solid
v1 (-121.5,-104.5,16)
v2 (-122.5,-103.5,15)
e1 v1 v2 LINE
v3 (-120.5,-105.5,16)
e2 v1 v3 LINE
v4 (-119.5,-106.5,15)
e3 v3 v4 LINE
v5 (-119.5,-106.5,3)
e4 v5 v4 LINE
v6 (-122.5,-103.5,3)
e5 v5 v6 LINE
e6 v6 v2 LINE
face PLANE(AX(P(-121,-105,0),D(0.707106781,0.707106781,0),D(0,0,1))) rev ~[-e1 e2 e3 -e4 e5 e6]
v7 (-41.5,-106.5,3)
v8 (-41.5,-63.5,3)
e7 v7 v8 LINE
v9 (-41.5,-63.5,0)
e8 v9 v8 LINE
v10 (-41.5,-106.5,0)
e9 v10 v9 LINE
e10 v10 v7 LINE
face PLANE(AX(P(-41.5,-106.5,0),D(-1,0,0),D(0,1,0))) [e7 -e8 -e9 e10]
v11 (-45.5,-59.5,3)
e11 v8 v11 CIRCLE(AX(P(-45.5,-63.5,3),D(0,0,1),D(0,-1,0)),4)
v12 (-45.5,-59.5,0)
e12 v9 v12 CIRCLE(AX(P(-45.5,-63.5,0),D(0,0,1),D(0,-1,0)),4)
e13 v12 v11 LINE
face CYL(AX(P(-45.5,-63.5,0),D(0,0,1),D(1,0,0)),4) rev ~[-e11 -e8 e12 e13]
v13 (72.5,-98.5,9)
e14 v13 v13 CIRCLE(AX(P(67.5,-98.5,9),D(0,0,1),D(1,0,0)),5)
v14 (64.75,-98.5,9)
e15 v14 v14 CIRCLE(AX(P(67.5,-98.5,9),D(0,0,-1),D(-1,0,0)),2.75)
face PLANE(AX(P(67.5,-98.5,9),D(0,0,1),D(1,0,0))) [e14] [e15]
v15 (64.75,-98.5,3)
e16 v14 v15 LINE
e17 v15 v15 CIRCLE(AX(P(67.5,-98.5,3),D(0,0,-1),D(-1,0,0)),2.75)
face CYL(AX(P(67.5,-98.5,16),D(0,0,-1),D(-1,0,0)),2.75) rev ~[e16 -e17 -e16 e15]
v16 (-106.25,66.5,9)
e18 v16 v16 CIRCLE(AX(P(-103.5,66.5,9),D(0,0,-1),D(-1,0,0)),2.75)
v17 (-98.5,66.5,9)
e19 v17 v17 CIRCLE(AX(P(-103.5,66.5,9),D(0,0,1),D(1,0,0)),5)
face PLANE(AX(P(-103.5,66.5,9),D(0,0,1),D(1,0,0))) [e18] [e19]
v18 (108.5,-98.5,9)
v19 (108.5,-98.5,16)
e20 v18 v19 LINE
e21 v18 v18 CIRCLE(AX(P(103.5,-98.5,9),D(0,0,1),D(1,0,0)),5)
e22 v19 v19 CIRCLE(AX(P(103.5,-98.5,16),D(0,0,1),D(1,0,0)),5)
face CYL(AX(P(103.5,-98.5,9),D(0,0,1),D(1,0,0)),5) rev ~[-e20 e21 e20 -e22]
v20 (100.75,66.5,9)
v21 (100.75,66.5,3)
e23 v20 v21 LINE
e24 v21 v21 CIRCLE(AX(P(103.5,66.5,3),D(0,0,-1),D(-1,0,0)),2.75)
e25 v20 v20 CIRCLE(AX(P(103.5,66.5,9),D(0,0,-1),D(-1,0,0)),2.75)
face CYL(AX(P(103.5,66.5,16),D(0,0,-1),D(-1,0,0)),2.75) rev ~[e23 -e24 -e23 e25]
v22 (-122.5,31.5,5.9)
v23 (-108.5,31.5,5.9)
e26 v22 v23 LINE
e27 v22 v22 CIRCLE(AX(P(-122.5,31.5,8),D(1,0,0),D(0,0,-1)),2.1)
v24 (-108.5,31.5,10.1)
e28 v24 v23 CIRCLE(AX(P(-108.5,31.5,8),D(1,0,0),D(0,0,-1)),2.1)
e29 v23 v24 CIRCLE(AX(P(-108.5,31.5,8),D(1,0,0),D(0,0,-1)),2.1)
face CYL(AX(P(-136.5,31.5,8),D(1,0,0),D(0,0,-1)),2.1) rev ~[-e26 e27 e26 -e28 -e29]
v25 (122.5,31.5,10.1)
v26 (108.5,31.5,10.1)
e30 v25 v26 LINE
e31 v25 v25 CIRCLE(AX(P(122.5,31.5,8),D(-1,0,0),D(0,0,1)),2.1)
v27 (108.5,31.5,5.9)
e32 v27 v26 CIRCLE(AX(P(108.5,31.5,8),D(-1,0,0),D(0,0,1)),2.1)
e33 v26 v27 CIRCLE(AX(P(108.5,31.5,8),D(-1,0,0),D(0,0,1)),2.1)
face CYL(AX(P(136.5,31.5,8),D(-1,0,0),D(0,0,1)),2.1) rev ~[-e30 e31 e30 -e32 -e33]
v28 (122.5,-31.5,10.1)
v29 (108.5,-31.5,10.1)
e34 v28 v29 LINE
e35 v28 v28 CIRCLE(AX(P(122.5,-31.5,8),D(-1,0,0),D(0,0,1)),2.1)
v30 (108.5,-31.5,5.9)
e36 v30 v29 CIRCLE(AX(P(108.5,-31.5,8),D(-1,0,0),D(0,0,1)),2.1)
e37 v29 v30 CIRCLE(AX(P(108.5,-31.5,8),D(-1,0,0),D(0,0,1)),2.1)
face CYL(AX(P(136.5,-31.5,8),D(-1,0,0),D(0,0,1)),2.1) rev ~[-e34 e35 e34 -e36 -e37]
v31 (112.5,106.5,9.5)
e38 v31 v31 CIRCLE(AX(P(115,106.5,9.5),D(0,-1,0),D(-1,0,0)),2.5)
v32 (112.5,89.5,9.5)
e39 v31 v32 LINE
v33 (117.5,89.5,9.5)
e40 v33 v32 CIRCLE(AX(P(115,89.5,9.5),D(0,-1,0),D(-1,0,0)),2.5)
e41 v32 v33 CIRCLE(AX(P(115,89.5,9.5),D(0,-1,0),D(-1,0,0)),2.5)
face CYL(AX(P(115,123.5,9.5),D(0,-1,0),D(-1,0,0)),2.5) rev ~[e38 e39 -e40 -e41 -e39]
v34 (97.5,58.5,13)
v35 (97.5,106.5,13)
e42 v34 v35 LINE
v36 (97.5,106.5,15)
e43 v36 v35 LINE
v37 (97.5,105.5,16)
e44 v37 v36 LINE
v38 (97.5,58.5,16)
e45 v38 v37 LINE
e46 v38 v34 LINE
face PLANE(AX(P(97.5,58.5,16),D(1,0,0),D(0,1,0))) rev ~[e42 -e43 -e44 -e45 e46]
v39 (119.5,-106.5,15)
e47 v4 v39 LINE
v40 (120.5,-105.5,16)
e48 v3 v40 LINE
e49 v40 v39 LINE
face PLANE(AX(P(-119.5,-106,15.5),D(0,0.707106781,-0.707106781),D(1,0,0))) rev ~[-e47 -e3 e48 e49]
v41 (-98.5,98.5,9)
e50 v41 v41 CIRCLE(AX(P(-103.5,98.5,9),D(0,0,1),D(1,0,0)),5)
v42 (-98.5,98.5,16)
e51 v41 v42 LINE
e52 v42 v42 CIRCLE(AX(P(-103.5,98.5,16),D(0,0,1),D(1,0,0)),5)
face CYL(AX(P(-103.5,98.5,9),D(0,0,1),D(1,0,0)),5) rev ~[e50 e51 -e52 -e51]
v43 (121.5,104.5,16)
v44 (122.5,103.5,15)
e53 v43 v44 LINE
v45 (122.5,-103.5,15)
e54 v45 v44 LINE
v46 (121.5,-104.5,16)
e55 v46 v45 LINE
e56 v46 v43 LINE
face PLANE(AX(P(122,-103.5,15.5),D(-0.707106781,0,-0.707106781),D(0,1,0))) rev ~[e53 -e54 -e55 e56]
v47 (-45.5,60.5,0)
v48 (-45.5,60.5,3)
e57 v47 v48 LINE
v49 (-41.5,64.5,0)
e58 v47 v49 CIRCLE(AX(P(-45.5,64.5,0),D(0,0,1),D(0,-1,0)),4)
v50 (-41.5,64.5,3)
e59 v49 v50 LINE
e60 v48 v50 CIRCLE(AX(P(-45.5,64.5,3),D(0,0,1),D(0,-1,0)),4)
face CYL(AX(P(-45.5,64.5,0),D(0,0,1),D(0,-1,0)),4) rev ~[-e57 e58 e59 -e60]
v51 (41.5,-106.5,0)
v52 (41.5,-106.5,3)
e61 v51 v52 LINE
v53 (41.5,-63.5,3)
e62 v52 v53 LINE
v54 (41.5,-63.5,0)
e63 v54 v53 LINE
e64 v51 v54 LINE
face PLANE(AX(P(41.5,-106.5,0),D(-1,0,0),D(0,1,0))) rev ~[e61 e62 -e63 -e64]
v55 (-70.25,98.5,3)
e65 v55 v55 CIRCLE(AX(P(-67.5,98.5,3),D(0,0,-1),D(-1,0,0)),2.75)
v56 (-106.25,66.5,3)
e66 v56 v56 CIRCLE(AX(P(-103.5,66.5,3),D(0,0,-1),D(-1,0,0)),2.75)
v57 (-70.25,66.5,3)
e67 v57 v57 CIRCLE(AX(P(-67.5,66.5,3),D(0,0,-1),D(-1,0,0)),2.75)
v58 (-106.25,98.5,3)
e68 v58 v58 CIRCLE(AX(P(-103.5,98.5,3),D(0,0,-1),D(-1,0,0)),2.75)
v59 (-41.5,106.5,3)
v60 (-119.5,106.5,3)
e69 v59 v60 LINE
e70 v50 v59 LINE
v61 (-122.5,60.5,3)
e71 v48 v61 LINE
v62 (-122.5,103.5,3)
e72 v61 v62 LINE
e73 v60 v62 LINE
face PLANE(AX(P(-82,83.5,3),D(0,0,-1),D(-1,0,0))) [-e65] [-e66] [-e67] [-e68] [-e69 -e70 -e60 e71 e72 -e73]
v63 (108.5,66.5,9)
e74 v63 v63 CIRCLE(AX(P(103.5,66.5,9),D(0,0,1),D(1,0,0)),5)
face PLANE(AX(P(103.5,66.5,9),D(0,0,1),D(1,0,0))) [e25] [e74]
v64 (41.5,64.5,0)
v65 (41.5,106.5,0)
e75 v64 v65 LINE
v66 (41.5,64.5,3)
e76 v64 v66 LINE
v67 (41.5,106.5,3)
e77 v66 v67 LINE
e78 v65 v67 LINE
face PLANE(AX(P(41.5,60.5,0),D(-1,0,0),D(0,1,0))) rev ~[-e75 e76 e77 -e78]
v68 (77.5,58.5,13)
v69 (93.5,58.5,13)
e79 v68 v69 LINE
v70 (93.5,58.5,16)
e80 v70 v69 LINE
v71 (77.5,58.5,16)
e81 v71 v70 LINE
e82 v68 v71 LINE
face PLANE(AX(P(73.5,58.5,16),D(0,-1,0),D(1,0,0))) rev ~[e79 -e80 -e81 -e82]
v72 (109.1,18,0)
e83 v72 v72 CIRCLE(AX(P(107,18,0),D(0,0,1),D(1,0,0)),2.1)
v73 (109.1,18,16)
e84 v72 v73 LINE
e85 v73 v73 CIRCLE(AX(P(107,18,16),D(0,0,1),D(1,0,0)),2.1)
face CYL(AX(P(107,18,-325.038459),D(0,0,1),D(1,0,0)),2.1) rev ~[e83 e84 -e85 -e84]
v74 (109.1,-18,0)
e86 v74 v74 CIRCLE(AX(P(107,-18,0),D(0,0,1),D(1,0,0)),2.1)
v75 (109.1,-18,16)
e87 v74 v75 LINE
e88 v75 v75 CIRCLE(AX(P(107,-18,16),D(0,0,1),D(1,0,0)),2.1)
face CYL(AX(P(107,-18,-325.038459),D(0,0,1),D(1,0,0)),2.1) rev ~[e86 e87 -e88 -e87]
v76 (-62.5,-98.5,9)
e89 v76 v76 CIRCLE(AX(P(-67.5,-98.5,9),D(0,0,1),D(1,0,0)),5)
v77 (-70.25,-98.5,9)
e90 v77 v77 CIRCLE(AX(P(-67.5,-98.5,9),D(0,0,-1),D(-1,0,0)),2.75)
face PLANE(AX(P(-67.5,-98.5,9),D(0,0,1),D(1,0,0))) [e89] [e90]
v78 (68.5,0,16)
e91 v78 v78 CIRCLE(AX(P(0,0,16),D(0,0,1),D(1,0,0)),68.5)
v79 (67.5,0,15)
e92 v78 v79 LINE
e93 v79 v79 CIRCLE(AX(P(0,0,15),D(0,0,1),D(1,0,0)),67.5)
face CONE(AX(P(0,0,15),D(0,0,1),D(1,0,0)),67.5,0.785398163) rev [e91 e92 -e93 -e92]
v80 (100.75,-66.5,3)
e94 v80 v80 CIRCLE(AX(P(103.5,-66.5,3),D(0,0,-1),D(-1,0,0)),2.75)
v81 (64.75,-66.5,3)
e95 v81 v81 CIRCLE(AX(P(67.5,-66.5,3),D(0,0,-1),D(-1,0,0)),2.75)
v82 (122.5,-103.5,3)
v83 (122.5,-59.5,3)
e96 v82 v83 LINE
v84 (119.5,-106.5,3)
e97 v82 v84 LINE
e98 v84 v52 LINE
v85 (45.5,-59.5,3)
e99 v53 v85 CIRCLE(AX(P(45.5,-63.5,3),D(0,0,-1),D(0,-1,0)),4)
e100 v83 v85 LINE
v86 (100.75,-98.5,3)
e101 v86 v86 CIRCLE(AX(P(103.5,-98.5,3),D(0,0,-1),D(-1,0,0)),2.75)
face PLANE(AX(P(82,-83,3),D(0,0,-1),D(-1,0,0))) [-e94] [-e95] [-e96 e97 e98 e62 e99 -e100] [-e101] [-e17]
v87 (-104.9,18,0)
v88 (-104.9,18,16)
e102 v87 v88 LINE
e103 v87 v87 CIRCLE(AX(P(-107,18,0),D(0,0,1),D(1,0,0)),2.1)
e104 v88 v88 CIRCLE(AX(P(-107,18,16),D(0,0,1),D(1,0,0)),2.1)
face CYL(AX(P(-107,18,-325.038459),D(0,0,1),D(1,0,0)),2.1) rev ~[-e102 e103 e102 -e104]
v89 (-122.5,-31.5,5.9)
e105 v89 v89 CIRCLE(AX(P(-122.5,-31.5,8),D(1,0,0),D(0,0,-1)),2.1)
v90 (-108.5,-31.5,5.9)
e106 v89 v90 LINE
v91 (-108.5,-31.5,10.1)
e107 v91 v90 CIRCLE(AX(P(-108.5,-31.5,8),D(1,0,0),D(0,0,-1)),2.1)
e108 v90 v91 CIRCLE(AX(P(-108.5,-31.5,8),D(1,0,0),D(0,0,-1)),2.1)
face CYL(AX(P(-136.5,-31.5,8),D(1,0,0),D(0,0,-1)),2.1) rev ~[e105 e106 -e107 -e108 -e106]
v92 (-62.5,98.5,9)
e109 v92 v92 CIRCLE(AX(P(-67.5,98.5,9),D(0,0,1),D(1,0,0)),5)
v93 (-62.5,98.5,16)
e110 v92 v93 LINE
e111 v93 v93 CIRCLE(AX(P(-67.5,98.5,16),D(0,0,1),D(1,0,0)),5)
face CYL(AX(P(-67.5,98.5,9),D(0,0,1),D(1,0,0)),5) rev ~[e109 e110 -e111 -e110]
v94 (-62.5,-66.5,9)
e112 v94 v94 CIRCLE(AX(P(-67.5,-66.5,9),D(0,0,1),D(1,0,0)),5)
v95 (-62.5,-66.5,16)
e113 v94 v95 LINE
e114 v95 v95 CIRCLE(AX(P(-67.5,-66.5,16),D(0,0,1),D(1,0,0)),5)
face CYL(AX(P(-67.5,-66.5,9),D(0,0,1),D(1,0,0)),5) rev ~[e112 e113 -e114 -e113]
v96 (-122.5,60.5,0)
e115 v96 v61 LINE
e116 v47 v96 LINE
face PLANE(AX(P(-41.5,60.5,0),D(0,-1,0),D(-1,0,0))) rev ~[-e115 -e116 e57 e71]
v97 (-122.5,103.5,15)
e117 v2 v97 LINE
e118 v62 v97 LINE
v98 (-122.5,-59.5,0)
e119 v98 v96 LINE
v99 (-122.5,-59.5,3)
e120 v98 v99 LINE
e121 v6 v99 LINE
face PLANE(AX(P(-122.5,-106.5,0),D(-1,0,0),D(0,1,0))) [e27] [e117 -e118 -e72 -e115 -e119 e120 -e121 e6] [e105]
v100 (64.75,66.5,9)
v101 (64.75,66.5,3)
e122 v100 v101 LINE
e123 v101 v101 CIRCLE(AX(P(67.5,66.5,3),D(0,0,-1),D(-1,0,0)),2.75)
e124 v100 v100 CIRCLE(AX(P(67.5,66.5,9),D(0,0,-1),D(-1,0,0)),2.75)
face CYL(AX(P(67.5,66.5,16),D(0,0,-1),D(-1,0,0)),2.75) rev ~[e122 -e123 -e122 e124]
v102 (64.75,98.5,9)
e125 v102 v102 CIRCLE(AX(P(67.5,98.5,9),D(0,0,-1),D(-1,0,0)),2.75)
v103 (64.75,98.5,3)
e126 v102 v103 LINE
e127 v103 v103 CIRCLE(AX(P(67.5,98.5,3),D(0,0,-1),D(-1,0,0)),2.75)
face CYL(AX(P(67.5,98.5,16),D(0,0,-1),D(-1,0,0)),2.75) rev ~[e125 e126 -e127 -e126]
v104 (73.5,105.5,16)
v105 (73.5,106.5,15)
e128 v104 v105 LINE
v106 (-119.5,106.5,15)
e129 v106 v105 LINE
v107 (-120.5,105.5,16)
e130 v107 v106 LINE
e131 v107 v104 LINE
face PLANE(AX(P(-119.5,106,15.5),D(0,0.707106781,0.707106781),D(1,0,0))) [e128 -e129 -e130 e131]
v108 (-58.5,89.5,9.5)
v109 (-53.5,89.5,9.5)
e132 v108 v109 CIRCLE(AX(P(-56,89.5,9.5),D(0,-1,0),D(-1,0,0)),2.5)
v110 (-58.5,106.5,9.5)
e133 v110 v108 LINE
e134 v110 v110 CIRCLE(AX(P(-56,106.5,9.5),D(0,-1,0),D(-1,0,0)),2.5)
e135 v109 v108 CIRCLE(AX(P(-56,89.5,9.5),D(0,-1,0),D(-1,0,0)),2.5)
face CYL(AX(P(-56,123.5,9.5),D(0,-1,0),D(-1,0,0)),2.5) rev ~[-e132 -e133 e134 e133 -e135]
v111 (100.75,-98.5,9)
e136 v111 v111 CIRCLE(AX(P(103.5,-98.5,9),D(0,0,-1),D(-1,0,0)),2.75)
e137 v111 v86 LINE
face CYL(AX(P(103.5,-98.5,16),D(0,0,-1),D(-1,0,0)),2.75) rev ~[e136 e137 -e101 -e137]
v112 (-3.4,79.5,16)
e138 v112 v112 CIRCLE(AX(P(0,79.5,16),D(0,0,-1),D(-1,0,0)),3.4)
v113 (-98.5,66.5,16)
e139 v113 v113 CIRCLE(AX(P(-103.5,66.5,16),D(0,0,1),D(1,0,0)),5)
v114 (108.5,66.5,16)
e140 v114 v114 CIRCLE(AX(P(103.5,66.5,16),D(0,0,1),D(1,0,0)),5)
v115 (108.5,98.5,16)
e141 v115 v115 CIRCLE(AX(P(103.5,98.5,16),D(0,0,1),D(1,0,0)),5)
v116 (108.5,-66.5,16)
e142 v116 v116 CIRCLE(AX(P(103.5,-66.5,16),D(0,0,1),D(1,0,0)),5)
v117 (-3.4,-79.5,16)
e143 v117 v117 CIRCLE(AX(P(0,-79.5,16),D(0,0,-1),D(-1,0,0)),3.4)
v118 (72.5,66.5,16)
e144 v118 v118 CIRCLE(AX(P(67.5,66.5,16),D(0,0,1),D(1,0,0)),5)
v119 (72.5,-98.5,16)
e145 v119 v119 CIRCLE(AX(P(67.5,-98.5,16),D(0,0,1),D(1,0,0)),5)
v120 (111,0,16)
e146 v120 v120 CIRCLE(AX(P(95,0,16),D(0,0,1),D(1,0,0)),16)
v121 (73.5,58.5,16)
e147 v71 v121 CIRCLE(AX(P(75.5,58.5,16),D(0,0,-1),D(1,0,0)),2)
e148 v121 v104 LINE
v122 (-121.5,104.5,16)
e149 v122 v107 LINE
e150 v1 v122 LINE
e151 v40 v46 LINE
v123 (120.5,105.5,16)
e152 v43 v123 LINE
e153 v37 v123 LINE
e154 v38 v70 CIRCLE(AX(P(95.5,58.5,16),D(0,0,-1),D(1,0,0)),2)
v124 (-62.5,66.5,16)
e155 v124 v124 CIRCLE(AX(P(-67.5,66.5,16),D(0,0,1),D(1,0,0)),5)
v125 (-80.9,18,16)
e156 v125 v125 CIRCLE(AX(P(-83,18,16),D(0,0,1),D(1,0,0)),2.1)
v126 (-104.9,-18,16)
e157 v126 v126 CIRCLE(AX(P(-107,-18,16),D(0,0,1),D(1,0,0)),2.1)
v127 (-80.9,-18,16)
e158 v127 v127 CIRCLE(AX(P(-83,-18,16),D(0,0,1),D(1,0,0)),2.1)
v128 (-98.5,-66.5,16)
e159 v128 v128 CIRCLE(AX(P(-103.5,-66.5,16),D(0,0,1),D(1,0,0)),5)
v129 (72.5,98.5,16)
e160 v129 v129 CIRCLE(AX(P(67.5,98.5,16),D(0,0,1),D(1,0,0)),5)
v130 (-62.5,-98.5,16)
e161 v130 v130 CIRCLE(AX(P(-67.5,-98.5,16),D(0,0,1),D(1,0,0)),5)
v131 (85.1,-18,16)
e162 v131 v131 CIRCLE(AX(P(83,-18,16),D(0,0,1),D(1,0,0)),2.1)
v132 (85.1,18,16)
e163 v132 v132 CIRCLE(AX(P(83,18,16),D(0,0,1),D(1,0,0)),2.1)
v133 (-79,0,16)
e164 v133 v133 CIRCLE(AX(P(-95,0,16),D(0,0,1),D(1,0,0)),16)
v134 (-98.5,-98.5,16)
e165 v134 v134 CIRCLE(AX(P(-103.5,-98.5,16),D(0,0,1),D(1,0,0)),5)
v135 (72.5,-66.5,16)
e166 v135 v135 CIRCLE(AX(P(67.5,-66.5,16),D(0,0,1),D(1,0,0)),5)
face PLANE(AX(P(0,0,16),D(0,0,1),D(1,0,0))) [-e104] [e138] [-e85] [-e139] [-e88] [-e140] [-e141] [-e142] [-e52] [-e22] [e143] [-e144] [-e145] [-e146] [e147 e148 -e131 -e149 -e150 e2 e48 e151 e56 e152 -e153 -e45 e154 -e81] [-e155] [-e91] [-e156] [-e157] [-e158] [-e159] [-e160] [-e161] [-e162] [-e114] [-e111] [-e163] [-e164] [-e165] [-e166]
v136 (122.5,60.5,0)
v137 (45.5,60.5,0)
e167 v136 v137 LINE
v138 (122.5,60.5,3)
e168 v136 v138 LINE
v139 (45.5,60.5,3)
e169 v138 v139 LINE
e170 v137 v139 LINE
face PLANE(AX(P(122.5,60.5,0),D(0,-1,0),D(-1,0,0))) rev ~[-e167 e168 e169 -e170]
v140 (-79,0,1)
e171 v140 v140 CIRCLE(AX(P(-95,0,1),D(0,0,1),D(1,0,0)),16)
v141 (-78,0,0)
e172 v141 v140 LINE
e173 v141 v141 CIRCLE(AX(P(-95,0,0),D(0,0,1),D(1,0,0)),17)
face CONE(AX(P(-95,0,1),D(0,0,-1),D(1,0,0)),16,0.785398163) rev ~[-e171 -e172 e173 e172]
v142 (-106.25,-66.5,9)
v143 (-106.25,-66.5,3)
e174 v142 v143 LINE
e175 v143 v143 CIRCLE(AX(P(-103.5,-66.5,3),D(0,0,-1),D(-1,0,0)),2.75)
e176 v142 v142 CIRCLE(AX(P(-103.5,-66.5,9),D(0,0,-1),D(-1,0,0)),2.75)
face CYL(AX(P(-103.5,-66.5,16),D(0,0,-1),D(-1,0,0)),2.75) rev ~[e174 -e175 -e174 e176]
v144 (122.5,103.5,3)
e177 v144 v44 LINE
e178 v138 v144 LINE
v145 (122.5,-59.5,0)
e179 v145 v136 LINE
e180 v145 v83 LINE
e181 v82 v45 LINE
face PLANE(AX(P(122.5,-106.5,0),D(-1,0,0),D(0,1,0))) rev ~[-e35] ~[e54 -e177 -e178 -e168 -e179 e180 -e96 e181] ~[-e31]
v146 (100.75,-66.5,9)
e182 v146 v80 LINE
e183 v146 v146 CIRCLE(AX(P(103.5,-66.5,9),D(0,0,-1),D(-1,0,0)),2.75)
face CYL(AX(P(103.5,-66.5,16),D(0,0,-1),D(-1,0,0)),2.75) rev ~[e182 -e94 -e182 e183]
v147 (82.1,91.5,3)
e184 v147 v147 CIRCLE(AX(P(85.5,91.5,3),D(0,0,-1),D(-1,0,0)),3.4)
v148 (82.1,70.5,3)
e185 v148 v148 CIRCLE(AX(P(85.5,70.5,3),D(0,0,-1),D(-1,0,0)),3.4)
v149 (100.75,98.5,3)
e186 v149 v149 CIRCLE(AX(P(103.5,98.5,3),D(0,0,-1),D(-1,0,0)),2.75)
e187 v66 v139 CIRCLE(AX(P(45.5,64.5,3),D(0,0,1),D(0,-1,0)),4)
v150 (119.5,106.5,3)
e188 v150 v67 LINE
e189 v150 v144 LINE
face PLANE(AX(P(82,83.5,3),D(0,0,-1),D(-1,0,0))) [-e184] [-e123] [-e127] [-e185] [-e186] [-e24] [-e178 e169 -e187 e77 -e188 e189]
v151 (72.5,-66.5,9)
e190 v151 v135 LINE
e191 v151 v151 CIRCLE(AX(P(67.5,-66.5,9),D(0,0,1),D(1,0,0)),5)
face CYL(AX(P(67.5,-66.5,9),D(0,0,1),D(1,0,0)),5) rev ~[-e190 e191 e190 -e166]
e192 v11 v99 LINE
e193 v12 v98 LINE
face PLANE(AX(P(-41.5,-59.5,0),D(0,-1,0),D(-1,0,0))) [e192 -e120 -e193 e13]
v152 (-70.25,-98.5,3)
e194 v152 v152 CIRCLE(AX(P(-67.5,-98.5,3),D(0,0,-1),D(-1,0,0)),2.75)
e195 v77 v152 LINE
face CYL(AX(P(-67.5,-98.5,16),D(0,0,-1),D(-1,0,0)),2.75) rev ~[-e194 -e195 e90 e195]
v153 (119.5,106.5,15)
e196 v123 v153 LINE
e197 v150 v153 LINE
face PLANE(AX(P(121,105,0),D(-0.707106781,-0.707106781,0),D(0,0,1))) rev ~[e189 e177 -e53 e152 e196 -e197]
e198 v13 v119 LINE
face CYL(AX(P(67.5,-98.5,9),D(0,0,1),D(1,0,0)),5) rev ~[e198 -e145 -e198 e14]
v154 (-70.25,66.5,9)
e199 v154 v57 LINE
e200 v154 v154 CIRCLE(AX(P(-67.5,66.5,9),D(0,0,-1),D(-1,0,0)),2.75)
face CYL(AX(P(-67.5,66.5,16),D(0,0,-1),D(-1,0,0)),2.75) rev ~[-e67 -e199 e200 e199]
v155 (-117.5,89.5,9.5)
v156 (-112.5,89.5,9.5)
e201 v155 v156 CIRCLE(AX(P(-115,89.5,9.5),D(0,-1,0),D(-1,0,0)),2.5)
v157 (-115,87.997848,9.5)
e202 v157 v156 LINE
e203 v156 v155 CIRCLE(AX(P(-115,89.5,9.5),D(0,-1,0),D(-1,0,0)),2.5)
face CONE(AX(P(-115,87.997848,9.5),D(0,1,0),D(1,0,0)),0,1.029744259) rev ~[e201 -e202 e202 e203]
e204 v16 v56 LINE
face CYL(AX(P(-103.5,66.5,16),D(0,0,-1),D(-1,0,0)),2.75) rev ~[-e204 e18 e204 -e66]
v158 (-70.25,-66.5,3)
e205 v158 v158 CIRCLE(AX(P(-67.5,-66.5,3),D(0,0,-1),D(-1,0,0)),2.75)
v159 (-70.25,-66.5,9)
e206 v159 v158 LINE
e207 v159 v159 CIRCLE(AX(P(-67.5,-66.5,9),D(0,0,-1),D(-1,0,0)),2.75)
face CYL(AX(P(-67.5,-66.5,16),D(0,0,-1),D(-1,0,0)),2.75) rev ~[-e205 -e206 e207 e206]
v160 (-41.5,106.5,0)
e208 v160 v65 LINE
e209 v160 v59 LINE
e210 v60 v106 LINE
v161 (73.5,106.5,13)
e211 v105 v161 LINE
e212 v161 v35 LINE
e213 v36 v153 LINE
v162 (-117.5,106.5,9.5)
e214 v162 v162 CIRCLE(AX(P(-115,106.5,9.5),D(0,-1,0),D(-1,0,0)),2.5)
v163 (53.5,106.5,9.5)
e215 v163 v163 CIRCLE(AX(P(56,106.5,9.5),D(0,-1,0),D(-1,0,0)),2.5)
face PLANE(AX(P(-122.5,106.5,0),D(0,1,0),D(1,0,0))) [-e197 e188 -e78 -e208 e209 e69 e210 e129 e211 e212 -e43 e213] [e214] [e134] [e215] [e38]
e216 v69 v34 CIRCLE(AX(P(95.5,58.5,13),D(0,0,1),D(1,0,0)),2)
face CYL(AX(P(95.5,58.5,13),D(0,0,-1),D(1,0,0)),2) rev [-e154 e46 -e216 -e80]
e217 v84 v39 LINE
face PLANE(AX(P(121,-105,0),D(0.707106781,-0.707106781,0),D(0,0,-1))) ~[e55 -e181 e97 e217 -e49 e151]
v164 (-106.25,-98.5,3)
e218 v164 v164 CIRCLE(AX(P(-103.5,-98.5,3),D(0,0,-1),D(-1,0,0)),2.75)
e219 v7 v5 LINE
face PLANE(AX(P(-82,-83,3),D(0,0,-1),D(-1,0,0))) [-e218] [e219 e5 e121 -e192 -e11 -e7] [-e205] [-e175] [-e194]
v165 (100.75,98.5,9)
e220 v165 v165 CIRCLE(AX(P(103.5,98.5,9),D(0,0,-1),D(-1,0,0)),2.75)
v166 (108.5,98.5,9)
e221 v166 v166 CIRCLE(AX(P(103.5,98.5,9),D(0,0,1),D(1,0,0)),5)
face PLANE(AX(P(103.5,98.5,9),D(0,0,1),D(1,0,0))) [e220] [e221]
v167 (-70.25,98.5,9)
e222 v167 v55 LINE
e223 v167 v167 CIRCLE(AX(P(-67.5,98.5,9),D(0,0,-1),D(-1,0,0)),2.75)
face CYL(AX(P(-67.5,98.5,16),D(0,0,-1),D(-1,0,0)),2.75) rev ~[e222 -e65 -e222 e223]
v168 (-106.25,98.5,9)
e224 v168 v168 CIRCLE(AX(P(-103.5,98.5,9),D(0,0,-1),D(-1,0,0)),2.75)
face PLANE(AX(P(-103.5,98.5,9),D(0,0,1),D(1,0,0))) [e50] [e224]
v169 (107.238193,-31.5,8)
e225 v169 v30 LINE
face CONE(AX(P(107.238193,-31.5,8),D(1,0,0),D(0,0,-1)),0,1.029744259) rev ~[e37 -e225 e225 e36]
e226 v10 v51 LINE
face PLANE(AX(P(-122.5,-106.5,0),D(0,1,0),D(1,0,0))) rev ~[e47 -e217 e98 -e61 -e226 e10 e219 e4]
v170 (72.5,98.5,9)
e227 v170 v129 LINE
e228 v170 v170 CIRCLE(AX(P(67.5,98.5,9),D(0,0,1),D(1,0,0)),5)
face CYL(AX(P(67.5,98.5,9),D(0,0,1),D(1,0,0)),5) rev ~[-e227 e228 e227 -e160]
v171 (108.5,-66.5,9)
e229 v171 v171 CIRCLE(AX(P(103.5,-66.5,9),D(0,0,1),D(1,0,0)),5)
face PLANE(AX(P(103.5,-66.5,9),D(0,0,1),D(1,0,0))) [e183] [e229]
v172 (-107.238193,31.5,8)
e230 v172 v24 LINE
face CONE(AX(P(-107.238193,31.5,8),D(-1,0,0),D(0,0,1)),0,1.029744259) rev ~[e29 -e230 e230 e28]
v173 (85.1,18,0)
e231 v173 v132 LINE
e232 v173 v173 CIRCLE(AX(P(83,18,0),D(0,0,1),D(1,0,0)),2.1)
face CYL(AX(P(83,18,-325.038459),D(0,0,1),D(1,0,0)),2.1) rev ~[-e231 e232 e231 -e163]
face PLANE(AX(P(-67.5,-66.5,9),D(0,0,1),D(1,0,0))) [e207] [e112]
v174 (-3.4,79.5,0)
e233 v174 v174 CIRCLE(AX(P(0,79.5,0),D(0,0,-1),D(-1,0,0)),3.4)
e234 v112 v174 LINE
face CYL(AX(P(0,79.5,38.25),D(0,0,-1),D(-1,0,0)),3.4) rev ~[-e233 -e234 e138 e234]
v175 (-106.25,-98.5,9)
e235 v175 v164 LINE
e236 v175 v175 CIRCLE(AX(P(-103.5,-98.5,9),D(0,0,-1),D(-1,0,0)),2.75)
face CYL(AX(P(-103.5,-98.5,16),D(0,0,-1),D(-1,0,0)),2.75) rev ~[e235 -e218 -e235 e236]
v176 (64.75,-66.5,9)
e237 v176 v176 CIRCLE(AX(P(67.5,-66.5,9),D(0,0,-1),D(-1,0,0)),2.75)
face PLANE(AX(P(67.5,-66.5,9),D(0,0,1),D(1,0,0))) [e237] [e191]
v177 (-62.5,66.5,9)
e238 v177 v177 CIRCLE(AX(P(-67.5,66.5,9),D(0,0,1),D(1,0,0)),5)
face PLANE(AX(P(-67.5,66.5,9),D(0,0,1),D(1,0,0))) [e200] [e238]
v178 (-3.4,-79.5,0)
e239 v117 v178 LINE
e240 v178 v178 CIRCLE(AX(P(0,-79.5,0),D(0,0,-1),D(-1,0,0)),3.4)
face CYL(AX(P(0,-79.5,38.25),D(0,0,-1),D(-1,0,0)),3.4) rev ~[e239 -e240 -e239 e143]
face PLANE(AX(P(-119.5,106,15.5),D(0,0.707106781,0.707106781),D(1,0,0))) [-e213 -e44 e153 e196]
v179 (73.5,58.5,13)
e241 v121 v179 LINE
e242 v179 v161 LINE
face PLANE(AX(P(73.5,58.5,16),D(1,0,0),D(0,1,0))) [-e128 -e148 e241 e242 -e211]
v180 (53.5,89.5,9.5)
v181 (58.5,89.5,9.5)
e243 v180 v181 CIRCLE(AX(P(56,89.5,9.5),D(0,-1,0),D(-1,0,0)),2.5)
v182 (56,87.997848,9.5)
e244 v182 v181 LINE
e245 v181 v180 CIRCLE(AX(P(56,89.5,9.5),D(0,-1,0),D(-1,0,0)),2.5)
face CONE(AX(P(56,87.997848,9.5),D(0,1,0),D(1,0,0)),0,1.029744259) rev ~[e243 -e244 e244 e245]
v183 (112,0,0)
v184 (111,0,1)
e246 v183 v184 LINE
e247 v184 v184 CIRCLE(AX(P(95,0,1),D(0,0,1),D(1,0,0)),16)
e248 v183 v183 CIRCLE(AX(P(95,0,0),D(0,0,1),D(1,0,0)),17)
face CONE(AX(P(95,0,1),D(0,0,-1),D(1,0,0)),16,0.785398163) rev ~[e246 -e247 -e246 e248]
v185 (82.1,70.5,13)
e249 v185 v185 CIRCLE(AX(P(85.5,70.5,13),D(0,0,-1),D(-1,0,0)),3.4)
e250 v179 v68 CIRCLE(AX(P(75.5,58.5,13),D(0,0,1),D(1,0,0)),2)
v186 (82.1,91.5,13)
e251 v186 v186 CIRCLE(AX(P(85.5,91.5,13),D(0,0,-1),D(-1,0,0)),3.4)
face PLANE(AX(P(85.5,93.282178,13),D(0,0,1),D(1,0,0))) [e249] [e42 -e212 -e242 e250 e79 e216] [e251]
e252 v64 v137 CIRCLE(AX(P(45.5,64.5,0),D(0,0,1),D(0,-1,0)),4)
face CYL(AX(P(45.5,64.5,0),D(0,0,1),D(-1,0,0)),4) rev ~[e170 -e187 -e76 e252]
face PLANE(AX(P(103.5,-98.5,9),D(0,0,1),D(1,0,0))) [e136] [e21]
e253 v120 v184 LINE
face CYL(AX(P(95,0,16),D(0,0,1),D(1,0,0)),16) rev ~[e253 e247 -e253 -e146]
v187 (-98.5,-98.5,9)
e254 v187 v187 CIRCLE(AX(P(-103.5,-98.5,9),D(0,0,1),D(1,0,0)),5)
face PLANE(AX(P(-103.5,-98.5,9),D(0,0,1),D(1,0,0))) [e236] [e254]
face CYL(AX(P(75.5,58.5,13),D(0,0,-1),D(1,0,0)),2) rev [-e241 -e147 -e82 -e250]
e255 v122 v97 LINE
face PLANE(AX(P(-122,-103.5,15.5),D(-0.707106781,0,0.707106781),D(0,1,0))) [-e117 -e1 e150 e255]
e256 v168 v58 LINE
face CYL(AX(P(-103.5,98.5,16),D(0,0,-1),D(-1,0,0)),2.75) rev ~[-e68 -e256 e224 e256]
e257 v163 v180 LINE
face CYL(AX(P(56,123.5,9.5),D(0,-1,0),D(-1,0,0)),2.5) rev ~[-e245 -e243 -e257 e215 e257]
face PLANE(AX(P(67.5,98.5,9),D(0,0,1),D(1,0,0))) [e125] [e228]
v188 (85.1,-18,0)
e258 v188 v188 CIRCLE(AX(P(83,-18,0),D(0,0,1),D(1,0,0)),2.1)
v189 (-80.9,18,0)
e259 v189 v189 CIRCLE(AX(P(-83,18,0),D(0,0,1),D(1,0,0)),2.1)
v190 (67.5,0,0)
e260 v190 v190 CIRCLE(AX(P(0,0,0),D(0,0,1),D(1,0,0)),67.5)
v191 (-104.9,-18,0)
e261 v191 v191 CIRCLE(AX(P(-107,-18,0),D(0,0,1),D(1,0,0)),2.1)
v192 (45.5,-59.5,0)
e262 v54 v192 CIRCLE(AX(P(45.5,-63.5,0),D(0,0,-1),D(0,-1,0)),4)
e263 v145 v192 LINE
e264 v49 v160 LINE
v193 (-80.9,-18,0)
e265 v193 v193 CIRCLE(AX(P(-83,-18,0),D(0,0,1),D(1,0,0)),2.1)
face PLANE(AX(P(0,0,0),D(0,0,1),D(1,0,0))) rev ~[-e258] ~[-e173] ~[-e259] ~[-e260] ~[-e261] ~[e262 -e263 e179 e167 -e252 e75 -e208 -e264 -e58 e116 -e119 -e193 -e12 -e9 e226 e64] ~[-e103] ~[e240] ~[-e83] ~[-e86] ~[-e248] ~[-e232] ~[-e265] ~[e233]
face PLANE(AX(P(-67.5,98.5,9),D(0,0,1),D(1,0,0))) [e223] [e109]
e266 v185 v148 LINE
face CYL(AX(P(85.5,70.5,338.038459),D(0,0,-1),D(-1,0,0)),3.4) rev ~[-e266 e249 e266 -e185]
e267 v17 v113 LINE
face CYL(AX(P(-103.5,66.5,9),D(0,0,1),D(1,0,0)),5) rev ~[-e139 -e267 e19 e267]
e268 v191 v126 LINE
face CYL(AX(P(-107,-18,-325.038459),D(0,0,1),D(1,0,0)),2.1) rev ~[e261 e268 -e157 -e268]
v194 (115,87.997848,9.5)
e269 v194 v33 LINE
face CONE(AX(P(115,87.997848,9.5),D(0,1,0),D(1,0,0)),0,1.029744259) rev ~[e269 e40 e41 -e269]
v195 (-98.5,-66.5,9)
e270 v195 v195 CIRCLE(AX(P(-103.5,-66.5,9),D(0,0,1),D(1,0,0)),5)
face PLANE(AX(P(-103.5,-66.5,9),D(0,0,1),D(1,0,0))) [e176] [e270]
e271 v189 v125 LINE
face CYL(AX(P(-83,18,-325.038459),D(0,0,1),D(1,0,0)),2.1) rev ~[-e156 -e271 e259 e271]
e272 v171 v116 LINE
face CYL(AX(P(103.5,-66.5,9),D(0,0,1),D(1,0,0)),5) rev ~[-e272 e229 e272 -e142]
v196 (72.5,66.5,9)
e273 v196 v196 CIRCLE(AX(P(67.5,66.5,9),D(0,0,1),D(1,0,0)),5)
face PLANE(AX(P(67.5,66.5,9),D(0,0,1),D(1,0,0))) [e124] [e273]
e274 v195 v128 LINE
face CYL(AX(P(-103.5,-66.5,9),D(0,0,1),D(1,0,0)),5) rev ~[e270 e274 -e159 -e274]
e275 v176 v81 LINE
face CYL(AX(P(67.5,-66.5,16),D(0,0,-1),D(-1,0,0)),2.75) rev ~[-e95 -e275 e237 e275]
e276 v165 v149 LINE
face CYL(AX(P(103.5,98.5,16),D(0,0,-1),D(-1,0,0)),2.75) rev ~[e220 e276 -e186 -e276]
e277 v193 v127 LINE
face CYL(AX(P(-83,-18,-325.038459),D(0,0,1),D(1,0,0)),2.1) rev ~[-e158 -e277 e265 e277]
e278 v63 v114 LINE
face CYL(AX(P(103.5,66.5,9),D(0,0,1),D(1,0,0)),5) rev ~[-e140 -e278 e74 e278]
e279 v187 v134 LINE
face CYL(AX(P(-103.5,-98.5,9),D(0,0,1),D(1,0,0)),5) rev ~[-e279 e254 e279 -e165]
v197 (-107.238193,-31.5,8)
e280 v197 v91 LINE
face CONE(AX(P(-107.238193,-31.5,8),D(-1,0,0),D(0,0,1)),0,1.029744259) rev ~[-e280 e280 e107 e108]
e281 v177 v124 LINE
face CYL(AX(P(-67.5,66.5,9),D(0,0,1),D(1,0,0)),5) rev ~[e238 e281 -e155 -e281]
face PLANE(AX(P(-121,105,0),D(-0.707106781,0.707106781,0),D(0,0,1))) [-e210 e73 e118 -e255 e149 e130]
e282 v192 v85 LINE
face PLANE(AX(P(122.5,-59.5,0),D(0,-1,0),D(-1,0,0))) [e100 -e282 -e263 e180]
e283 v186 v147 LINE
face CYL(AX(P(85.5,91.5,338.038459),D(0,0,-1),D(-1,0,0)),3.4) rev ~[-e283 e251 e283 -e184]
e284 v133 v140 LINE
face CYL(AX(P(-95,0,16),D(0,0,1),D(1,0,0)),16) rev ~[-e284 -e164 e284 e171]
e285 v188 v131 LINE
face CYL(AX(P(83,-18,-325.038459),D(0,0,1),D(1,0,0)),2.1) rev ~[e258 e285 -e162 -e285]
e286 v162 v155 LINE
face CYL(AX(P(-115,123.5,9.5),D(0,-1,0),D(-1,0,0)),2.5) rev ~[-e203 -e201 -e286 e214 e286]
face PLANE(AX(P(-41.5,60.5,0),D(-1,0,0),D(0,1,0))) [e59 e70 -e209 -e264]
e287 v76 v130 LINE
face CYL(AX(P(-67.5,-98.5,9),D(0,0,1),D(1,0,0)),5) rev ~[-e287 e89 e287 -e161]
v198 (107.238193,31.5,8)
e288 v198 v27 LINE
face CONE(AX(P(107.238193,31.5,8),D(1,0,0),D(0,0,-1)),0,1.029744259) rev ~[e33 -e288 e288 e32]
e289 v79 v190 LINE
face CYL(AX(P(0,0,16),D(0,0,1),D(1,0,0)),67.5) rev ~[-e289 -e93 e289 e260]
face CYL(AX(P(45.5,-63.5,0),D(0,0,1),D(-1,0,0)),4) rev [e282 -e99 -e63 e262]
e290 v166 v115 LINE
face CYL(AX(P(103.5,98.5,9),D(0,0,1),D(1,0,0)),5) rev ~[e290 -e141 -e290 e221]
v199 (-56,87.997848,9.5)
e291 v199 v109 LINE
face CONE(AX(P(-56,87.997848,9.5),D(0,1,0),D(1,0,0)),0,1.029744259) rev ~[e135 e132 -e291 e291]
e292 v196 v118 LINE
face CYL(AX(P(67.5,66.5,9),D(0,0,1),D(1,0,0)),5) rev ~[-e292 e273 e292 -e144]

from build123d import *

# Parameters (mm, degrees)
SKETCH1_W                                           = 245
SKETCH1_H                                           = 213
BOSS_EXTRUDE1_DEPTH                                 = 16
CHAMFER1_SIZE                                       = 3
SKETCH3_R                                           = 67.5
CUT_EXTRUDE2_DEPTH                                  = 100
CHAMFER2_SIZE                                       = 1
SKETCH4_R                                           = 16
CUT_EXTRUDE3_DEPTH                                  = 159
CHAMFER3_SIZE                                       = 1
SKETCH5_W                                           = 81
SKETCH5_H                                           = 46
SKETCH5_H_2                                         = 47
CUT_EXTRUDE4_DEPTH                                  = 3
FILLET1_R                                           = 4
HOLE_SIZE_PER_SOCKET_HEAD_CAP_SCREW_TYP_D           = 5.5
HOLE_SIZE_PER_SOCKET_HEAD_CAP_SCREW_TYP_CBORE_D     = 10
HOLE_SIZE_PER_SOCKET_HEAD_CAP_SCREW_TYP_CBORE_DEPTH = 7
M8_TAPPED_HOLE1_D                                   = 6.8
M8_TAPPED_HOLE1_DEPTH                               = 22.25
M8_TAPPED_HOLE1_TIP                                 = 2.042926105
SKETCH10_W                                          = 24
SKETCH10_H                                          = 69.564356815
CUT_EXTRUDE5_DEPTH                                  = 3
SKETCH11_R                                          = 2
CUT_EXTRUDE6_DEPTH                                  = 38
M8_TAPPED_HOLE2_D                                   = 6.8
M6_TAPPED_HOLE1_D                                   = 5
M6_TAPPED_HOLE1_DEPTH                               = 17
M6_TAPPED_HOLE1_TIP                                 = 1.502151548
M5_TAPPED_HOLE1_D                                   = 4.2
M5_TAPPED_HOLE1_DEPTH                               = 14
M5_TAPPED_HOLE1_TIP                                 = 1.2618073
M5_TAPPED_HOLE2_D                                   = 4.2
M5_TAPPED_HOLE2_DEPTH                               = 14
M5_TAPPED_HOLE2_TIP                                 = 1.2618073
M5_TAPPED_HOLE3_D                                   = 4.2
CHAMFER4_SIZE                                       = 1


with BuildPart() as part:
    # Sketch1 → Boss-Extrude1 (new body)
    with BuildSketch(Plane.XY):
        Rectangle(SKETCH1_W, SKETCH1_H)
    extrude(amount=BOSS_EXTRUDE1_DEPTH)

    # Chamfer1
    chamfer1_edges = [part.edges().sort_by_distance(p)[0] for p in [
        (122.5, -106.5, 8),
        (-122.5, -106.5, 8),
        (-122.5, 106.5, 8),
        (122.5, 106.5, 8),
    ]]
    chamfer(chamfer1_edges, length=CHAMFER1_SIZE)

    # Sketch3 → Cut-Extrude2 (cut)
    with BuildSketch(Plane.XY.offset(16)):
        Circle(SKETCH3_R)
    extrude(amount=-CUT_EXTRUDE2_DEPTH, mode=Mode.SUBTRACT)

    # Chamfer2
    chamfer2_edges = [part.edges().sort_by_distance(p)[0] for p in [
        (-67.5, 0, 16),
    ]]
    chamfer(chamfer2_edges, length=CHAMFER2_SIZE)

    # Sketch4 → Cut-Extrude3 (cut)
    with BuildSketch(Plane.XY.offset(16)):
        with Locations((-95, 0)):
            Circle(SKETCH4_R)
        with Locations((95, 0)):
            Circle(SKETCH4_R)
    extrude(amount=-CUT_EXTRUDE3_DEPTH, mode=Mode.SUBTRACT)

    # Chamfer3
    chamfer3_edges = [part.edges().sort_by_distance(p)[0] for p in [
        (0, 106.5, 16),
        (122.5, 0, 16),
        (-122.5, 0, 16),
        (0, -106.5, 16),
    ]]
    chamfer(chamfer3_edges, length=CHAMFER3_SIZE)

    # Sketch5 → Cut-Extrude4 (cut)
    with BuildSketch(Plane(origin=(0, 0, 0), x_dir=(-1, 0, 0), z_dir=(0, 0, -1))):
        with Locations((-82, 83.5)):
            Rectangle(SKETCH5_W, SKETCH5_H)
        with Locations((-82, -83)):
            Rectangle(SKETCH5_W, SKETCH5_H_2)
        with Locations((82, -83)):
            Rectangle(SKETCH5_W, SKETCH5_H_2)
        with Locations((82, 83.5)):
            Rectangle(SKETCH5_W, SKETCH5_H)
    extrude(amount=-CUT_EXTRUDE4_DEPTH, mode=Mode.SUBTRACT)

    # Fillet1
    fillet1_edges = [part.edges().sort_by_distance(p)[0] for p in [
        (-41.5, 60.5, 1.5),
        (-41.5, -59.5, 1.5),
        (41.5, -59.5, 1.5),
        (41.5, 60.5, 1.5),
    ]]
    fillet(fillet1_edges, radius=FILLET1_R)

    # Hole size (per socket head cap screw type)0 (through all)
    with Locations(Plane.XY.offset(16)):
        with Locations((-103.5, -98.5), (-67.5, -98.5), (-67.5, -66.5), (-103.5, -66.5), (67.5, -66.5), (67.5, -98.5), (103.5, -98.5), (103.5, -66.5), (67.5, 98.5), (67.5, 66.5), (103.5, 66.5), (103.5, 98.5), (-103.5, 98.5), (-103.5, 66.5), (-67.5, 66.5), (-67.5, 98.5)):
            CounterBoreHole(HOLE_SIZE_PER_SOCKET_HEAD_CAP_SCREW_TYP_D / 2, HOLE_SIZE_PER_SOCKET_HEAD_CAP_SCREW_TYP_CBORE_D / 2, HOLE_SIZE_PER_SOCKET_HEAD_CAP_SCREW_TYP_CBORE_DEPTH)

    # M8 Tapped Hole1
    with Locations(Plane.XY.offset(16)):
        with Locations((0, 79.5), (0, -79.5)):
            Hole(M8_TAPPED_HOLE1_D / 2, depth=M8_TAPPED_HOLE1_DEPTH)
            with Locations((0, 0, -(M8_TAPPED_HOLE1_DEPTH + M8_TAPPED_HOLE1_TIP / 2))):  # 118° drill point
                Cone(0, M8_TAPPED_HOLE1_D / 2, M8_TAPPED_HOLE1_TIP, mode=Mode.SUBTRACT)

    # Sketch10 → Cut-Extrude5 (cut)
    with BuildSketch(Plane.XY.offset(16)):
        with Locations((85.5, 93.282178407)):
            Rectangle(SKETCH10_W, SKETCH10_H)
    extrude(amount=-CUT_EXTRUDE5_DEPTH, mode=Mode.SUBTRACT)

    # Sketch11 → Cut-Extrude6 (cut)
    with BuildSketch(Plane.XY.offset(13)):
        with Locations((75.5, 58.5)):
            Circle(SKETCH11_R)
        with Locations((95.5, 58.5)):
            Circle(SKETCH11_R)
    extrude(amount=CUT_EXTRUDE6_DEPTH, mode=Mode.SUBTRACT)

    # M8 Tapped Hole2 (through all)
    with Locations(Plane.XY.offset(13)):
        with Locations((85.5, 70.5), (85.5, 91.5)):
            Hole(M8_TAPPED_HOLE2_D / 2)

    # M6 Tapped Hole1
    with Locations(Plane(origin=(0, 106.5, 0), x_dir=(1, 0, 0), z_dir=(0, 1, 0))):
        with Locations((56, -9.5), (115, -9.5), (-56, -9.5), (-115, -9.5)):
            Hole(M6_TAPPED_HOLE1_D / 2, depth=M6_TAPPED_HOLE1_DEPTH)
            with Locations((0, 0, -(M6_TAPPED_HOLE1_DEPTH + M6_TAPPED_HOLE1_TIP / 2))):  # 118° drill point
                Cone(0, M6_TAPPED_HOLE1_D / 2, M6_TAPPED_HOLE1_TIP, mode=Mode.SUBTRACT)

    # M5 Tapped Hole1
    with Locations(Plane(origin=(122.5, 0, 0), x_dir=(0, 0, -1), z_dir=(1, 0, 0))):
        with Locations((-8, -31.5), (-8, 31.5)):
            Hole(M5_TAPPED_HOLE1_D / 2, depth=M5_TAPPED_HOLE1_DEPTH)
            with Locations((0, 0, -(M5_TAPPED_HOLE1_DEPTH + M5_TAPPED_HOLE1_TIP / 2))):  # 118° drill point
                Cone(0, M5_TAPPED_HOLE1_D / 2, M5_TAPPED_HOLE1_TIP, mode=Mode.SUBTRACT)

    # M5 Tapped Hole2
    with Locations(Plane.ZY.offset(122.5)):
        with Locations((8, 31.5), (8, -31.5)):
            Hole(M5_TAPPED_HOLE2_D / 2, depth=M5_TAPPED_HOLE2_DEPTH)
            with Locations((0, 0, -(M5_TAPPED_HOLE2_DEPTH + M5_TAPPED_HOLE2_TIP / 2))):  # 118° drill point
                Cone(0, M5_TAPPED_HOLE2_D / 2, M5_TAPPED_HOLE2_TIP, mode=Mode.SUBTRACT)

    # M5 Tapped Hole3 (through all)
    with Locations(Plane(origin=(0, 0, 0), x_dir=(-1, 0, 0), z_dir=(0, 0, -1))):
        with Locations((-107, 18), (-83, 18), (-83, -18), (-107, -18), (83, 18), (107, 18), (83, -18), (107, -18)):
            Hole(M5_TAPPED_HOLE3_D / 2)

    # Chamfer4
    chamfer4_edges = [part.edges().sort_by_distance(p)[0] for p in [
        (-111, 0, 0),
        (79, 0, 0),
    ]]
    chamfer(chamfer4_edges, length=CHAMFER4_SIZE)


solid = part.part
